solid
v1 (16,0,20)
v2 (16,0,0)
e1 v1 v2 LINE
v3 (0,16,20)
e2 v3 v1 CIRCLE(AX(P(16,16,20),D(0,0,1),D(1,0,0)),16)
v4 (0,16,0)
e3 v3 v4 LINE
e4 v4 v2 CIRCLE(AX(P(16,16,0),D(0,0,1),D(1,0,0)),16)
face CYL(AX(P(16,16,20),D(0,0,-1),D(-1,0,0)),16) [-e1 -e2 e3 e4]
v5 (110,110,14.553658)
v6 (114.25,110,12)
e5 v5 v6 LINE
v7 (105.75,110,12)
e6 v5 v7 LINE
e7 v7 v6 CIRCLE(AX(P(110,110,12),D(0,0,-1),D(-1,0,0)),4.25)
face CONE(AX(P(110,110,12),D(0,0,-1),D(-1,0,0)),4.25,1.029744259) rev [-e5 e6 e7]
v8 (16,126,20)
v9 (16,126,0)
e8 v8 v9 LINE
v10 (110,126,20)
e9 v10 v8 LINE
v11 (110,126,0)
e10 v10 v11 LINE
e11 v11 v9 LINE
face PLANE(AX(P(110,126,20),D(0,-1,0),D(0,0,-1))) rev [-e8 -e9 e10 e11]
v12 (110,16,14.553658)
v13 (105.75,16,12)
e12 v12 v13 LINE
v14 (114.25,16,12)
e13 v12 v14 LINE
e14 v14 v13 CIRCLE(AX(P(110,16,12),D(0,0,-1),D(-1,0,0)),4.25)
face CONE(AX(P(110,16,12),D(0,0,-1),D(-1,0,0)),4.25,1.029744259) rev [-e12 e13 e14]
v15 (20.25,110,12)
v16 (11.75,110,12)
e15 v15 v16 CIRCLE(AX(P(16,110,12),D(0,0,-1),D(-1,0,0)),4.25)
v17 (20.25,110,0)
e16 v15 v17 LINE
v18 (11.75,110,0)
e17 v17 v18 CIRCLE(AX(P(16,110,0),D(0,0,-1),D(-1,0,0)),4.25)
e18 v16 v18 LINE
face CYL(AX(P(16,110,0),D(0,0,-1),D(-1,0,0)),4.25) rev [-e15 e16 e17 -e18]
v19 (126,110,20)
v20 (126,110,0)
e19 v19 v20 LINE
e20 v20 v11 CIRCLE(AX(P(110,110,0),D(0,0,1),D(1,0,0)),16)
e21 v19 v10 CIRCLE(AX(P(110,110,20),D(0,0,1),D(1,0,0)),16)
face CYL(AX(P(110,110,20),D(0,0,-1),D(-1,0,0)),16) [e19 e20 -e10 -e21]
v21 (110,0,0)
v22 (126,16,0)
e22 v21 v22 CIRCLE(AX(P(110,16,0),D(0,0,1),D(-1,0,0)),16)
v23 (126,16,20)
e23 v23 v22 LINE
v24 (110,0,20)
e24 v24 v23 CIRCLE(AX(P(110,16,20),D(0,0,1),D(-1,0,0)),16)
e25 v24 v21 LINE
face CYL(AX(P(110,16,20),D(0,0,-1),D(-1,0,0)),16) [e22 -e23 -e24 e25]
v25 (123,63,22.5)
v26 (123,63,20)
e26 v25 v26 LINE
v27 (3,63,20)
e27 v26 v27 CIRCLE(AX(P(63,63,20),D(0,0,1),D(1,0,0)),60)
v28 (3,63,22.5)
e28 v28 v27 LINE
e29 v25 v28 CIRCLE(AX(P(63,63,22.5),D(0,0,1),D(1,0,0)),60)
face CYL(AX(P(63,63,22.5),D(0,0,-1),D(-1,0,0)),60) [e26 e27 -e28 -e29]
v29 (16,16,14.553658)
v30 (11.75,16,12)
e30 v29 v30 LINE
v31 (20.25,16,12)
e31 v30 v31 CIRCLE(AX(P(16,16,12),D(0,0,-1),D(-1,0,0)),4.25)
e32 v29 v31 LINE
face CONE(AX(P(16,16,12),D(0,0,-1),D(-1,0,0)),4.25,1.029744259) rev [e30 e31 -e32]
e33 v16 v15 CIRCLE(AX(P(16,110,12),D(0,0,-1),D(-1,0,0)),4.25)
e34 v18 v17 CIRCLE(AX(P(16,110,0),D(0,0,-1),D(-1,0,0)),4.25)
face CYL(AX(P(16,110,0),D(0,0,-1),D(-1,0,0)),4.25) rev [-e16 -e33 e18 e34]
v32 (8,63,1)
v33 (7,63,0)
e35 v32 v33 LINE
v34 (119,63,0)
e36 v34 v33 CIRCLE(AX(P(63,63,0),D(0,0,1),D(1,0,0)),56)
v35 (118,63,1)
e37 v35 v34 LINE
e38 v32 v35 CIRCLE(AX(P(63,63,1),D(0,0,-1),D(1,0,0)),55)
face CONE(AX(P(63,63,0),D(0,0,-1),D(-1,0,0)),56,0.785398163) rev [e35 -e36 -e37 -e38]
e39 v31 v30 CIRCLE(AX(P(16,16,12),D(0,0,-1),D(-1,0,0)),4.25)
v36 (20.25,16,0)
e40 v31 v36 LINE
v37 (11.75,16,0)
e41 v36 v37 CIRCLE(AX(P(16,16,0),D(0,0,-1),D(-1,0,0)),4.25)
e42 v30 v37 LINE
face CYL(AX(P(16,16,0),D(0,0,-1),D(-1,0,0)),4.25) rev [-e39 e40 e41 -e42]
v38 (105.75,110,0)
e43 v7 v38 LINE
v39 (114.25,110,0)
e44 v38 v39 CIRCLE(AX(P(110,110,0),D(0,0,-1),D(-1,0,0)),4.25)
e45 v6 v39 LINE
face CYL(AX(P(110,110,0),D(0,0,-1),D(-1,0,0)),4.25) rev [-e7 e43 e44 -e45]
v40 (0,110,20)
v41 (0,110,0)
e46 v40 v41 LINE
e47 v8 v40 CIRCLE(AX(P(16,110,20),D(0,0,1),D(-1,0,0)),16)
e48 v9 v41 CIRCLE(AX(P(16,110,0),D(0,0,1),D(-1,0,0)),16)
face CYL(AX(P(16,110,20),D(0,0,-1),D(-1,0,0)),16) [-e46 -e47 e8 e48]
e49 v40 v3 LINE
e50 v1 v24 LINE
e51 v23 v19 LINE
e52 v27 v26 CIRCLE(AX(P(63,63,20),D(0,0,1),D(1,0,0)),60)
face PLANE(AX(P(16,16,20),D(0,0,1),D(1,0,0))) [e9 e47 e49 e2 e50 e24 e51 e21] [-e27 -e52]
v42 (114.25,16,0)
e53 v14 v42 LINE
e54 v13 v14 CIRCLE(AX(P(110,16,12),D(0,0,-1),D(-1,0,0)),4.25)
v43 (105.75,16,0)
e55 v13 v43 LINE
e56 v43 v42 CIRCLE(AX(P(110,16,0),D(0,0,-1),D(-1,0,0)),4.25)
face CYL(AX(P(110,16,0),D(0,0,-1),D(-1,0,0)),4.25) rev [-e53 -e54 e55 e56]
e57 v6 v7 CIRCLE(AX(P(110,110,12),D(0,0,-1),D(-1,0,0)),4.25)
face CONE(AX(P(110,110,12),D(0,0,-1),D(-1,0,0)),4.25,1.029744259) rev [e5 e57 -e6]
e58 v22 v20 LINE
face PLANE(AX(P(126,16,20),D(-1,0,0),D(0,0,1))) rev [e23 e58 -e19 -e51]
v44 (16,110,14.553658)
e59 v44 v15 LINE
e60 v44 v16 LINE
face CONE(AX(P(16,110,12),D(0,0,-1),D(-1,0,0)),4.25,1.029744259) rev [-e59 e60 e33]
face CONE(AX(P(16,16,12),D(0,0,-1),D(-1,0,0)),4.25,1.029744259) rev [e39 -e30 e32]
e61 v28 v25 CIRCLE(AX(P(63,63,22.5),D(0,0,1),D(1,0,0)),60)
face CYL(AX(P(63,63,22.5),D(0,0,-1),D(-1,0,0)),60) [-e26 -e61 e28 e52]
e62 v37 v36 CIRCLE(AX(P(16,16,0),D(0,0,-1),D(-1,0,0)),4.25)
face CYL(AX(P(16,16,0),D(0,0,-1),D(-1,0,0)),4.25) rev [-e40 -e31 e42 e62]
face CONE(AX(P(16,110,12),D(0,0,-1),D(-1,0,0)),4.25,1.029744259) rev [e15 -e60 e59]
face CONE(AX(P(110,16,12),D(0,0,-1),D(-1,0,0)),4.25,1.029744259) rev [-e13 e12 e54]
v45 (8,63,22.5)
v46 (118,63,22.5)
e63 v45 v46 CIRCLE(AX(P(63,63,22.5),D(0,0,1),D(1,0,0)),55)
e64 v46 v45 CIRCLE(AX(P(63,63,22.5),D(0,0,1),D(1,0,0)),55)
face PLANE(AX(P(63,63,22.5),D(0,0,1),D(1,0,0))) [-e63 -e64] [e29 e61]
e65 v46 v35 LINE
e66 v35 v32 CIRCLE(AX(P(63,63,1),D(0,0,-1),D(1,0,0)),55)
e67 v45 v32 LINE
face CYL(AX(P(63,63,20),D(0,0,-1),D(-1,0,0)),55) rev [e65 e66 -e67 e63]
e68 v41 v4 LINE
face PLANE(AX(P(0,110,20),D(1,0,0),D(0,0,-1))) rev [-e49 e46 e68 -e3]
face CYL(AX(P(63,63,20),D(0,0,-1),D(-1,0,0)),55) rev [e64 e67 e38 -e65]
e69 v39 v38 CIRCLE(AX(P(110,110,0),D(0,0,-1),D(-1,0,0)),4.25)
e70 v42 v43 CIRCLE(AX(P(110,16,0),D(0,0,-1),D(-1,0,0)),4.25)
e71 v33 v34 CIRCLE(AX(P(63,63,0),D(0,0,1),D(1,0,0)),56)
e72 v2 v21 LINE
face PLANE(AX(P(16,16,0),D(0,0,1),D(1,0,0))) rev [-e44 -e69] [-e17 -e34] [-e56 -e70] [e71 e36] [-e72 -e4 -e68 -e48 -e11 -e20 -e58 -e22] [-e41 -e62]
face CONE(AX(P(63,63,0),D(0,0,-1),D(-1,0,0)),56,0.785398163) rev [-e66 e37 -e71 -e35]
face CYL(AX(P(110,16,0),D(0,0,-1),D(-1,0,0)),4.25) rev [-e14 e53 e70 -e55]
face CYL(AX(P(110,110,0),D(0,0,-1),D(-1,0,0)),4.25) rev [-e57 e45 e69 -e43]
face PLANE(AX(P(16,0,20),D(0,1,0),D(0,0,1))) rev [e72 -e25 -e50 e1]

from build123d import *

# Parameters (mm, degrees)
SKETCH1_R                  = 55
BOSS_EXTRUDE1_DEPTH        = 20
SKETCH2_R                  = 60
SKETCH2_R_2                = 55
BOSS_EXTRUDE2_DEPTH        = 2.5
M10X1_5_TAPPED_HOLE1_D     = 8.5
M10X1_5_TAPPED_HOLE1_DEPTH = 12
M10X1_5_TAPPED_HOLE1_TIP   = 2.553657631
CHAMFER1_SIZE              = 1


with BuildPart() as part:
    # Sketch1 → Boss-Extrude1 (new body)
    with BuildSketch(Plane.XY):
        with BuildLine():
            Line((16, 0), (110, 0))
            ThreePointArc((110, 0), (121.313708499, 4.686291501), (126, 16))
            Line((126, 16), (126, 110))
            ThreePointArc((126, 110), (121.313708499, 121.313708499), (110, 126))
            Line((110, 126), (16, 126))
            ThreePointArc((16, 126), (4.686291501, 121.313708499), (0, 110))
            Line((0, 110), (0, 16))
            ThreePointArc((0, 16), (4.686291501, 4.686291501), (16, 0))
        make_face()
        with Locations((63, 63)):
            Circle(SKETCH1_R, mode=Mode.SUBTRACT)
    extrude(amount=BOSS_EXTRUDE1_DEPTH)

    # Sketch2 → Boss-Extrude2 (add)
    with BuildSketch(Plane.XY.offset(20)):
        with Locations((63, 63)):
            Circle(SKETCH2_R)
        with Locations((63, 63)):
            Circle(SKETCH2_R_2, mode=Mode.SUBTRACT)
    extrude(amount=BOSS_EXTRUDE2_DEPTH)

    # M10x1.5 Tapped Hole1
    with Locations(Plane(origin=(110, 110, 0), x_dir=(-1, 0, 0), z_dir=(0, 0, -1))):
        with Locations((0, 0), (94, 0), (94, -94), (0, -94)):
            Hole(M10X1_5_TAPPED_HOLE1_D / 2, depth=M10X1_5_TAPPED_HOLE1_DEPTH)
            with Locations((0, 0, -(M10X1_5_TAPPED_HOLE1_DEPTH + M10X1_5_TAPPED_HOLE1_TIP / 2))):  # 118° drill point
                Cone(0, M10X1_5_TAPPED_HOLE1_D / 2, M10X1_5_TAPPED_HOLE1_TIP, mode=Mode.SUBTRACT)

    # Chamfer1
    chamfer1_edges = [part.edges().sort_by_distance(p)[0] for p in [
        (8, 63, 0),
    ]]
    chamfer(chamfer1_edges, length=CHAMFER1_SIZE)


solid = part.part
